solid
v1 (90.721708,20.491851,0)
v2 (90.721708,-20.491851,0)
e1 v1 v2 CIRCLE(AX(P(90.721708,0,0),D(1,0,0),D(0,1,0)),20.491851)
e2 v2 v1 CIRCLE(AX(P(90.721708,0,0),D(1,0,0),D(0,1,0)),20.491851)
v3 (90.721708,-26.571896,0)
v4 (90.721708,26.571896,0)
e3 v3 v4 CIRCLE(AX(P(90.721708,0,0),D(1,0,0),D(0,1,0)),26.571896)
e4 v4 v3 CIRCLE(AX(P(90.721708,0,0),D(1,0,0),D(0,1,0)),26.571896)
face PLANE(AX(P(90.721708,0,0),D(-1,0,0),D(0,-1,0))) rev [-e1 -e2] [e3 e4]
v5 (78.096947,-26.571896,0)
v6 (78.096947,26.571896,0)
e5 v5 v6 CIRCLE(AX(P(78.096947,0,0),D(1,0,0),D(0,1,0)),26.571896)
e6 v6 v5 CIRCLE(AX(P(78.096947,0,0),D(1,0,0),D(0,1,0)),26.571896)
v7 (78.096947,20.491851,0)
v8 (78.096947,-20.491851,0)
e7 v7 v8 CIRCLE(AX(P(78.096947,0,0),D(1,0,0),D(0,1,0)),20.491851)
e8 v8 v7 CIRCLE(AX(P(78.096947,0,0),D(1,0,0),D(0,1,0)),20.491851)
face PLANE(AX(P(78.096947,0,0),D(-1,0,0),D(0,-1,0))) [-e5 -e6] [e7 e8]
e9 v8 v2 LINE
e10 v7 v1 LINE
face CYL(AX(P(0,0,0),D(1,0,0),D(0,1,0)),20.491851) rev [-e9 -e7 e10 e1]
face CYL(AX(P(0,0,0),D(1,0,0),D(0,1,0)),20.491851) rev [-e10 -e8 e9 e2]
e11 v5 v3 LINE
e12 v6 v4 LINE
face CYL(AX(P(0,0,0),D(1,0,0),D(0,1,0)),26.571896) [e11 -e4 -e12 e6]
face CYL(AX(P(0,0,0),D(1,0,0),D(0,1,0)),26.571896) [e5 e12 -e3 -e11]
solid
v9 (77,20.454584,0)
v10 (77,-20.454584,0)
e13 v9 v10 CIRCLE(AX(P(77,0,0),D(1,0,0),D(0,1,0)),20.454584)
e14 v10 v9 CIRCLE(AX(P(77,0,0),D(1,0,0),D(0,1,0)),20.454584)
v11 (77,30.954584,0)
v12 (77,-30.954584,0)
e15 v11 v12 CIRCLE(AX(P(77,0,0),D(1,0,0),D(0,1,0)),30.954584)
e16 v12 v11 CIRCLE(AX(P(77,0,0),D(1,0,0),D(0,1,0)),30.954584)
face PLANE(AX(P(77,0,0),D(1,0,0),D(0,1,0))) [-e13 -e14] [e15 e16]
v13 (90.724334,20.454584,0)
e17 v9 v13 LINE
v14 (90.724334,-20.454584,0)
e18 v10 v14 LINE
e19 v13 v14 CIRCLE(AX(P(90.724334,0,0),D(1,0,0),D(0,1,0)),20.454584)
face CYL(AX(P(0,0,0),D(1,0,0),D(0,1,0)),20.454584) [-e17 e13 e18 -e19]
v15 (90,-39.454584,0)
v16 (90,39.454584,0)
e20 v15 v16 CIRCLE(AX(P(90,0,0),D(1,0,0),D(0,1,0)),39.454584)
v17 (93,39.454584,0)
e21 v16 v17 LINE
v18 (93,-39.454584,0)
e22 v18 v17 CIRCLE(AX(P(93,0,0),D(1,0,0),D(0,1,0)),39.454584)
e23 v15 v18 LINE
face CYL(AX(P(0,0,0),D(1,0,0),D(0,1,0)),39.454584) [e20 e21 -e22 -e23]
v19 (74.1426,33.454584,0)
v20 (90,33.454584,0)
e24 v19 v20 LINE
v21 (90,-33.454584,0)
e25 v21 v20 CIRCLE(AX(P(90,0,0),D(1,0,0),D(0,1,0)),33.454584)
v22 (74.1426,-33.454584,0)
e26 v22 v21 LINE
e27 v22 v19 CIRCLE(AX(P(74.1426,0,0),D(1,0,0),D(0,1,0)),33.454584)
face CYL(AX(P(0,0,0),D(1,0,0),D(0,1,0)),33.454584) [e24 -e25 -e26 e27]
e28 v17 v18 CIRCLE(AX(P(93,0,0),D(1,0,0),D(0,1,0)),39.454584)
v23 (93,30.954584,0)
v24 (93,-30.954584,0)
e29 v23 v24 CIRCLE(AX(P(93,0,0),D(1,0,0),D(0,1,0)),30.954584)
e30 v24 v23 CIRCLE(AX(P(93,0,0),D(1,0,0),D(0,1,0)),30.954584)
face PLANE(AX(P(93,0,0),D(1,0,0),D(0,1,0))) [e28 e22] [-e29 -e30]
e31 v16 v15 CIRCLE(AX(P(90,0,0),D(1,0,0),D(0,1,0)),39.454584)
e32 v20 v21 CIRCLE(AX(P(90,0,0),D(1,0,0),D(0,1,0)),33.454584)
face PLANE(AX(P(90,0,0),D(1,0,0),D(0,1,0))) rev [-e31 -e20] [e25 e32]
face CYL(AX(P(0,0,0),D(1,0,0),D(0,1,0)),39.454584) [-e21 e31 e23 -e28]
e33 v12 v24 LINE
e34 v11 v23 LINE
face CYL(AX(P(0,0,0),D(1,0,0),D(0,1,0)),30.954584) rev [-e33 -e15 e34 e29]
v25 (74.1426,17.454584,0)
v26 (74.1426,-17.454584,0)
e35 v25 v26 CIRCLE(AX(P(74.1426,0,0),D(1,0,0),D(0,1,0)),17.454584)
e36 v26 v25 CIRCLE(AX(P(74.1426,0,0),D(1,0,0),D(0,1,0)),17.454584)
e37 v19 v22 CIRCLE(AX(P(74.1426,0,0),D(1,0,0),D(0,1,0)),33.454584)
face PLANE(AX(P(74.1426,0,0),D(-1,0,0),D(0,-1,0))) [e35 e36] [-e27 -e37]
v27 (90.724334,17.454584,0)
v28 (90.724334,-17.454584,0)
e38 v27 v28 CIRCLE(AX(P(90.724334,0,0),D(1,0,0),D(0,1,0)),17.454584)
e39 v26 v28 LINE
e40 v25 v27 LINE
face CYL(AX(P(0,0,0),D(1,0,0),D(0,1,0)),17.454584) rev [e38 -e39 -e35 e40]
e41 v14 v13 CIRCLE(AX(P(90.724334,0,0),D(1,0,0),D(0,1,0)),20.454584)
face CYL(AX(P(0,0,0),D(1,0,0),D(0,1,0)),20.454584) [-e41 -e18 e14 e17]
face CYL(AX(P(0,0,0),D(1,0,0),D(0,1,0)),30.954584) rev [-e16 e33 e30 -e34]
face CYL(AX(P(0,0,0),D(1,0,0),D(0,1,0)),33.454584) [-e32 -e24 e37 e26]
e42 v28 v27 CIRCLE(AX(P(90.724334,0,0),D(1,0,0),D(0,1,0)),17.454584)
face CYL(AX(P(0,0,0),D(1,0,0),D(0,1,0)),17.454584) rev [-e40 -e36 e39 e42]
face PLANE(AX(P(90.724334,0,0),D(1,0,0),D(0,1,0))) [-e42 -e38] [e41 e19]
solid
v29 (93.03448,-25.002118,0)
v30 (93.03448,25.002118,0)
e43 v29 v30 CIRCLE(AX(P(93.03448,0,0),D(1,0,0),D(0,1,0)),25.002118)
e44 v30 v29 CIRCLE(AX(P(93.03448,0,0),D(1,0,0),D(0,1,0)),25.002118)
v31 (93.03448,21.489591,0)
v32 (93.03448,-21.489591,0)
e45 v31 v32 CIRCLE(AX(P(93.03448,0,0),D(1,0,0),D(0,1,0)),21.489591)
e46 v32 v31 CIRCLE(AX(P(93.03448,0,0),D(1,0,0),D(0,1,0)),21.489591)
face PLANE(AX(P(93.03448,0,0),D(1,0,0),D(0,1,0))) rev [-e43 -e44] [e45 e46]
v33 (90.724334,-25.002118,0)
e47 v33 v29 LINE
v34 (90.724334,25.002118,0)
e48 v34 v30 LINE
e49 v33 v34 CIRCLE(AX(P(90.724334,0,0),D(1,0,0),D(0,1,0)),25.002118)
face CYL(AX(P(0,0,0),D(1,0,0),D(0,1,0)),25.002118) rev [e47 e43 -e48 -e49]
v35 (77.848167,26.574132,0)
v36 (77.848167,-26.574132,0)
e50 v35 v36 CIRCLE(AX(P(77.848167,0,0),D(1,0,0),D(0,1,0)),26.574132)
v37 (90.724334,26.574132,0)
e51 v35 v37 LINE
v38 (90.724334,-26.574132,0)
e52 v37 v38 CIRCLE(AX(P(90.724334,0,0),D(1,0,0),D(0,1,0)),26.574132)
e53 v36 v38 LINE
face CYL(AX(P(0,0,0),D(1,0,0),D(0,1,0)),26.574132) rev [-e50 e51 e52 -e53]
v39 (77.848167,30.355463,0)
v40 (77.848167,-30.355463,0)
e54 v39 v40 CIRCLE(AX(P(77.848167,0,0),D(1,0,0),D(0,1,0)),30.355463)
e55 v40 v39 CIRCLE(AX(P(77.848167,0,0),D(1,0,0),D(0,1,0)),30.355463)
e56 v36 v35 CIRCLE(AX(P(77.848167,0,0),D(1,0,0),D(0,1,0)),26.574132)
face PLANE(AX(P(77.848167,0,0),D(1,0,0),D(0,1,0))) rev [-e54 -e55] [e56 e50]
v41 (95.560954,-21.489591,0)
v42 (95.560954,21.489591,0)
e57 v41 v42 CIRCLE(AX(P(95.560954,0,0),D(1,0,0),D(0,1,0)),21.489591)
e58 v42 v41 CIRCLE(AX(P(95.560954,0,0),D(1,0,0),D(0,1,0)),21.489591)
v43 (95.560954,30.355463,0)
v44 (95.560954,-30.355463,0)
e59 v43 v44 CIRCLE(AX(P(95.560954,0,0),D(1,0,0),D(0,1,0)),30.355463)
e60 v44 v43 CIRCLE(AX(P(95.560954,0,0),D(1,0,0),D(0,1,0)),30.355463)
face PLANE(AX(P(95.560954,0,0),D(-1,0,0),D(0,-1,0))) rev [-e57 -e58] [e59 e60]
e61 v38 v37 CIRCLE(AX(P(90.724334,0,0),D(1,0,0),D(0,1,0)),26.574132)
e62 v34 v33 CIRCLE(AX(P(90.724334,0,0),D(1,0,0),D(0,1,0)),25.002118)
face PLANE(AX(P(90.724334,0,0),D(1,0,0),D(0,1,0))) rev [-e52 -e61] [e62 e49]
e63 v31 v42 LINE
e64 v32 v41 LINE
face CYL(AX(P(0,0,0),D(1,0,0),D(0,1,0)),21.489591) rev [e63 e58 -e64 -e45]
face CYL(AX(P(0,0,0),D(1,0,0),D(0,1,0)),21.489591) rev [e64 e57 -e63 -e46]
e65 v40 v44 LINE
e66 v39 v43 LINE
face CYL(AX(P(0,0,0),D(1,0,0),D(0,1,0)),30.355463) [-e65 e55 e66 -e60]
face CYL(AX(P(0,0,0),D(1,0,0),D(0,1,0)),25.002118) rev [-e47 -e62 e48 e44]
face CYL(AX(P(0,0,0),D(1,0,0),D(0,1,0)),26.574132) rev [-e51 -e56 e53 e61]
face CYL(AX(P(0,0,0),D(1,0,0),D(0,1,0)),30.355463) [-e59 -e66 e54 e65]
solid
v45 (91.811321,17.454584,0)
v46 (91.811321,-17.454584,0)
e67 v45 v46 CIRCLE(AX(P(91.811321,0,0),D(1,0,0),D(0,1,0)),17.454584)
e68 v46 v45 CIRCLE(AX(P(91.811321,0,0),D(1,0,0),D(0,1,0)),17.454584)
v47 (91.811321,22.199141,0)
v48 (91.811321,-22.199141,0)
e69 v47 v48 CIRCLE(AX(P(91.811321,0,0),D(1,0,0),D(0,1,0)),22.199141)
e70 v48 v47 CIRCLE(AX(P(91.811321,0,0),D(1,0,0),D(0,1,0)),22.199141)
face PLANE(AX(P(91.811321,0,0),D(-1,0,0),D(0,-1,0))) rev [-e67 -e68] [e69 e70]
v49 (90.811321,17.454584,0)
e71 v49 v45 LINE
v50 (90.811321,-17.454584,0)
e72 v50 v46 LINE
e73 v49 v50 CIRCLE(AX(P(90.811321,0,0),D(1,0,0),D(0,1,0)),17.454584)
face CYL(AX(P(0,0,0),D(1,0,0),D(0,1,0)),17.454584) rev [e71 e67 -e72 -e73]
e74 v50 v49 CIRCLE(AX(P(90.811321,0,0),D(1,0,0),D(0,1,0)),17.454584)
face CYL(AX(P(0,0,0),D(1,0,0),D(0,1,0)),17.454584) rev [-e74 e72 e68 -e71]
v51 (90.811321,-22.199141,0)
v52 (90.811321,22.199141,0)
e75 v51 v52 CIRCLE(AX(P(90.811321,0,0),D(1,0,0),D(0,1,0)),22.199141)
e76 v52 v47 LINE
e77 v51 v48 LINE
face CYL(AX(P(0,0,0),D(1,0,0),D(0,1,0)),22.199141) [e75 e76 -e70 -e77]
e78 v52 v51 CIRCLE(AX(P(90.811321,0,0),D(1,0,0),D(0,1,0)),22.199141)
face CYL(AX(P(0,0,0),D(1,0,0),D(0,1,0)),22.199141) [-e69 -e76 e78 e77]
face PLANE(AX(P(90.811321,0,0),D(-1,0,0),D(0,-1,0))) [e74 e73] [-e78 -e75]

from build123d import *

# Parameters (mm, degrees)
SKETCH1_W   = 12.624761142
SKETCH1_H   = 6.080044682
SKETCH1_W_2 = 1
SKETCH1_H_2 = 4.744556516


with BuildPart() as part:
    # Sketch1 → Revolve1 (revolve)
    with BuildSketch(Plane.XY):
        Polygon((93, 39.45458405), (93, 33.45458405), (93, 30.95458405), (77, 30.95458405), (77, 20.45458405), (90.724333667, 20.45458405), (90.724333667, 17.45458405), (74.14259961, 17.45458405), (74.14259961, 33.45458405), (90, 33.45458405), (90, 39.45458405), align=None)
        Polygon((77.84816745, 30.355462664), (92, 30.355462664), (95.560954263, 30.355462664), (95.560954263, 21.489590566), (93.034479753, 21.489590566), (93.034479753, 25.002117737), (90.724333667, 25.002117737), (90.724333667, 26.574131723), (77.84816745, 26.574131723), align=None)
        with Locations((84.40932732, 23.531873601)):
            Rectangle(SKETCH1_W, SKETCH1_H)
        with Locations((91.311321069, 19.826862308)):
            Rectangle(SKETCH1_W_2, SKETCH1_H_2)
    revolve(axis=Axis((0, 0, 0), (-1, 0, 0)))


solid = part.part
